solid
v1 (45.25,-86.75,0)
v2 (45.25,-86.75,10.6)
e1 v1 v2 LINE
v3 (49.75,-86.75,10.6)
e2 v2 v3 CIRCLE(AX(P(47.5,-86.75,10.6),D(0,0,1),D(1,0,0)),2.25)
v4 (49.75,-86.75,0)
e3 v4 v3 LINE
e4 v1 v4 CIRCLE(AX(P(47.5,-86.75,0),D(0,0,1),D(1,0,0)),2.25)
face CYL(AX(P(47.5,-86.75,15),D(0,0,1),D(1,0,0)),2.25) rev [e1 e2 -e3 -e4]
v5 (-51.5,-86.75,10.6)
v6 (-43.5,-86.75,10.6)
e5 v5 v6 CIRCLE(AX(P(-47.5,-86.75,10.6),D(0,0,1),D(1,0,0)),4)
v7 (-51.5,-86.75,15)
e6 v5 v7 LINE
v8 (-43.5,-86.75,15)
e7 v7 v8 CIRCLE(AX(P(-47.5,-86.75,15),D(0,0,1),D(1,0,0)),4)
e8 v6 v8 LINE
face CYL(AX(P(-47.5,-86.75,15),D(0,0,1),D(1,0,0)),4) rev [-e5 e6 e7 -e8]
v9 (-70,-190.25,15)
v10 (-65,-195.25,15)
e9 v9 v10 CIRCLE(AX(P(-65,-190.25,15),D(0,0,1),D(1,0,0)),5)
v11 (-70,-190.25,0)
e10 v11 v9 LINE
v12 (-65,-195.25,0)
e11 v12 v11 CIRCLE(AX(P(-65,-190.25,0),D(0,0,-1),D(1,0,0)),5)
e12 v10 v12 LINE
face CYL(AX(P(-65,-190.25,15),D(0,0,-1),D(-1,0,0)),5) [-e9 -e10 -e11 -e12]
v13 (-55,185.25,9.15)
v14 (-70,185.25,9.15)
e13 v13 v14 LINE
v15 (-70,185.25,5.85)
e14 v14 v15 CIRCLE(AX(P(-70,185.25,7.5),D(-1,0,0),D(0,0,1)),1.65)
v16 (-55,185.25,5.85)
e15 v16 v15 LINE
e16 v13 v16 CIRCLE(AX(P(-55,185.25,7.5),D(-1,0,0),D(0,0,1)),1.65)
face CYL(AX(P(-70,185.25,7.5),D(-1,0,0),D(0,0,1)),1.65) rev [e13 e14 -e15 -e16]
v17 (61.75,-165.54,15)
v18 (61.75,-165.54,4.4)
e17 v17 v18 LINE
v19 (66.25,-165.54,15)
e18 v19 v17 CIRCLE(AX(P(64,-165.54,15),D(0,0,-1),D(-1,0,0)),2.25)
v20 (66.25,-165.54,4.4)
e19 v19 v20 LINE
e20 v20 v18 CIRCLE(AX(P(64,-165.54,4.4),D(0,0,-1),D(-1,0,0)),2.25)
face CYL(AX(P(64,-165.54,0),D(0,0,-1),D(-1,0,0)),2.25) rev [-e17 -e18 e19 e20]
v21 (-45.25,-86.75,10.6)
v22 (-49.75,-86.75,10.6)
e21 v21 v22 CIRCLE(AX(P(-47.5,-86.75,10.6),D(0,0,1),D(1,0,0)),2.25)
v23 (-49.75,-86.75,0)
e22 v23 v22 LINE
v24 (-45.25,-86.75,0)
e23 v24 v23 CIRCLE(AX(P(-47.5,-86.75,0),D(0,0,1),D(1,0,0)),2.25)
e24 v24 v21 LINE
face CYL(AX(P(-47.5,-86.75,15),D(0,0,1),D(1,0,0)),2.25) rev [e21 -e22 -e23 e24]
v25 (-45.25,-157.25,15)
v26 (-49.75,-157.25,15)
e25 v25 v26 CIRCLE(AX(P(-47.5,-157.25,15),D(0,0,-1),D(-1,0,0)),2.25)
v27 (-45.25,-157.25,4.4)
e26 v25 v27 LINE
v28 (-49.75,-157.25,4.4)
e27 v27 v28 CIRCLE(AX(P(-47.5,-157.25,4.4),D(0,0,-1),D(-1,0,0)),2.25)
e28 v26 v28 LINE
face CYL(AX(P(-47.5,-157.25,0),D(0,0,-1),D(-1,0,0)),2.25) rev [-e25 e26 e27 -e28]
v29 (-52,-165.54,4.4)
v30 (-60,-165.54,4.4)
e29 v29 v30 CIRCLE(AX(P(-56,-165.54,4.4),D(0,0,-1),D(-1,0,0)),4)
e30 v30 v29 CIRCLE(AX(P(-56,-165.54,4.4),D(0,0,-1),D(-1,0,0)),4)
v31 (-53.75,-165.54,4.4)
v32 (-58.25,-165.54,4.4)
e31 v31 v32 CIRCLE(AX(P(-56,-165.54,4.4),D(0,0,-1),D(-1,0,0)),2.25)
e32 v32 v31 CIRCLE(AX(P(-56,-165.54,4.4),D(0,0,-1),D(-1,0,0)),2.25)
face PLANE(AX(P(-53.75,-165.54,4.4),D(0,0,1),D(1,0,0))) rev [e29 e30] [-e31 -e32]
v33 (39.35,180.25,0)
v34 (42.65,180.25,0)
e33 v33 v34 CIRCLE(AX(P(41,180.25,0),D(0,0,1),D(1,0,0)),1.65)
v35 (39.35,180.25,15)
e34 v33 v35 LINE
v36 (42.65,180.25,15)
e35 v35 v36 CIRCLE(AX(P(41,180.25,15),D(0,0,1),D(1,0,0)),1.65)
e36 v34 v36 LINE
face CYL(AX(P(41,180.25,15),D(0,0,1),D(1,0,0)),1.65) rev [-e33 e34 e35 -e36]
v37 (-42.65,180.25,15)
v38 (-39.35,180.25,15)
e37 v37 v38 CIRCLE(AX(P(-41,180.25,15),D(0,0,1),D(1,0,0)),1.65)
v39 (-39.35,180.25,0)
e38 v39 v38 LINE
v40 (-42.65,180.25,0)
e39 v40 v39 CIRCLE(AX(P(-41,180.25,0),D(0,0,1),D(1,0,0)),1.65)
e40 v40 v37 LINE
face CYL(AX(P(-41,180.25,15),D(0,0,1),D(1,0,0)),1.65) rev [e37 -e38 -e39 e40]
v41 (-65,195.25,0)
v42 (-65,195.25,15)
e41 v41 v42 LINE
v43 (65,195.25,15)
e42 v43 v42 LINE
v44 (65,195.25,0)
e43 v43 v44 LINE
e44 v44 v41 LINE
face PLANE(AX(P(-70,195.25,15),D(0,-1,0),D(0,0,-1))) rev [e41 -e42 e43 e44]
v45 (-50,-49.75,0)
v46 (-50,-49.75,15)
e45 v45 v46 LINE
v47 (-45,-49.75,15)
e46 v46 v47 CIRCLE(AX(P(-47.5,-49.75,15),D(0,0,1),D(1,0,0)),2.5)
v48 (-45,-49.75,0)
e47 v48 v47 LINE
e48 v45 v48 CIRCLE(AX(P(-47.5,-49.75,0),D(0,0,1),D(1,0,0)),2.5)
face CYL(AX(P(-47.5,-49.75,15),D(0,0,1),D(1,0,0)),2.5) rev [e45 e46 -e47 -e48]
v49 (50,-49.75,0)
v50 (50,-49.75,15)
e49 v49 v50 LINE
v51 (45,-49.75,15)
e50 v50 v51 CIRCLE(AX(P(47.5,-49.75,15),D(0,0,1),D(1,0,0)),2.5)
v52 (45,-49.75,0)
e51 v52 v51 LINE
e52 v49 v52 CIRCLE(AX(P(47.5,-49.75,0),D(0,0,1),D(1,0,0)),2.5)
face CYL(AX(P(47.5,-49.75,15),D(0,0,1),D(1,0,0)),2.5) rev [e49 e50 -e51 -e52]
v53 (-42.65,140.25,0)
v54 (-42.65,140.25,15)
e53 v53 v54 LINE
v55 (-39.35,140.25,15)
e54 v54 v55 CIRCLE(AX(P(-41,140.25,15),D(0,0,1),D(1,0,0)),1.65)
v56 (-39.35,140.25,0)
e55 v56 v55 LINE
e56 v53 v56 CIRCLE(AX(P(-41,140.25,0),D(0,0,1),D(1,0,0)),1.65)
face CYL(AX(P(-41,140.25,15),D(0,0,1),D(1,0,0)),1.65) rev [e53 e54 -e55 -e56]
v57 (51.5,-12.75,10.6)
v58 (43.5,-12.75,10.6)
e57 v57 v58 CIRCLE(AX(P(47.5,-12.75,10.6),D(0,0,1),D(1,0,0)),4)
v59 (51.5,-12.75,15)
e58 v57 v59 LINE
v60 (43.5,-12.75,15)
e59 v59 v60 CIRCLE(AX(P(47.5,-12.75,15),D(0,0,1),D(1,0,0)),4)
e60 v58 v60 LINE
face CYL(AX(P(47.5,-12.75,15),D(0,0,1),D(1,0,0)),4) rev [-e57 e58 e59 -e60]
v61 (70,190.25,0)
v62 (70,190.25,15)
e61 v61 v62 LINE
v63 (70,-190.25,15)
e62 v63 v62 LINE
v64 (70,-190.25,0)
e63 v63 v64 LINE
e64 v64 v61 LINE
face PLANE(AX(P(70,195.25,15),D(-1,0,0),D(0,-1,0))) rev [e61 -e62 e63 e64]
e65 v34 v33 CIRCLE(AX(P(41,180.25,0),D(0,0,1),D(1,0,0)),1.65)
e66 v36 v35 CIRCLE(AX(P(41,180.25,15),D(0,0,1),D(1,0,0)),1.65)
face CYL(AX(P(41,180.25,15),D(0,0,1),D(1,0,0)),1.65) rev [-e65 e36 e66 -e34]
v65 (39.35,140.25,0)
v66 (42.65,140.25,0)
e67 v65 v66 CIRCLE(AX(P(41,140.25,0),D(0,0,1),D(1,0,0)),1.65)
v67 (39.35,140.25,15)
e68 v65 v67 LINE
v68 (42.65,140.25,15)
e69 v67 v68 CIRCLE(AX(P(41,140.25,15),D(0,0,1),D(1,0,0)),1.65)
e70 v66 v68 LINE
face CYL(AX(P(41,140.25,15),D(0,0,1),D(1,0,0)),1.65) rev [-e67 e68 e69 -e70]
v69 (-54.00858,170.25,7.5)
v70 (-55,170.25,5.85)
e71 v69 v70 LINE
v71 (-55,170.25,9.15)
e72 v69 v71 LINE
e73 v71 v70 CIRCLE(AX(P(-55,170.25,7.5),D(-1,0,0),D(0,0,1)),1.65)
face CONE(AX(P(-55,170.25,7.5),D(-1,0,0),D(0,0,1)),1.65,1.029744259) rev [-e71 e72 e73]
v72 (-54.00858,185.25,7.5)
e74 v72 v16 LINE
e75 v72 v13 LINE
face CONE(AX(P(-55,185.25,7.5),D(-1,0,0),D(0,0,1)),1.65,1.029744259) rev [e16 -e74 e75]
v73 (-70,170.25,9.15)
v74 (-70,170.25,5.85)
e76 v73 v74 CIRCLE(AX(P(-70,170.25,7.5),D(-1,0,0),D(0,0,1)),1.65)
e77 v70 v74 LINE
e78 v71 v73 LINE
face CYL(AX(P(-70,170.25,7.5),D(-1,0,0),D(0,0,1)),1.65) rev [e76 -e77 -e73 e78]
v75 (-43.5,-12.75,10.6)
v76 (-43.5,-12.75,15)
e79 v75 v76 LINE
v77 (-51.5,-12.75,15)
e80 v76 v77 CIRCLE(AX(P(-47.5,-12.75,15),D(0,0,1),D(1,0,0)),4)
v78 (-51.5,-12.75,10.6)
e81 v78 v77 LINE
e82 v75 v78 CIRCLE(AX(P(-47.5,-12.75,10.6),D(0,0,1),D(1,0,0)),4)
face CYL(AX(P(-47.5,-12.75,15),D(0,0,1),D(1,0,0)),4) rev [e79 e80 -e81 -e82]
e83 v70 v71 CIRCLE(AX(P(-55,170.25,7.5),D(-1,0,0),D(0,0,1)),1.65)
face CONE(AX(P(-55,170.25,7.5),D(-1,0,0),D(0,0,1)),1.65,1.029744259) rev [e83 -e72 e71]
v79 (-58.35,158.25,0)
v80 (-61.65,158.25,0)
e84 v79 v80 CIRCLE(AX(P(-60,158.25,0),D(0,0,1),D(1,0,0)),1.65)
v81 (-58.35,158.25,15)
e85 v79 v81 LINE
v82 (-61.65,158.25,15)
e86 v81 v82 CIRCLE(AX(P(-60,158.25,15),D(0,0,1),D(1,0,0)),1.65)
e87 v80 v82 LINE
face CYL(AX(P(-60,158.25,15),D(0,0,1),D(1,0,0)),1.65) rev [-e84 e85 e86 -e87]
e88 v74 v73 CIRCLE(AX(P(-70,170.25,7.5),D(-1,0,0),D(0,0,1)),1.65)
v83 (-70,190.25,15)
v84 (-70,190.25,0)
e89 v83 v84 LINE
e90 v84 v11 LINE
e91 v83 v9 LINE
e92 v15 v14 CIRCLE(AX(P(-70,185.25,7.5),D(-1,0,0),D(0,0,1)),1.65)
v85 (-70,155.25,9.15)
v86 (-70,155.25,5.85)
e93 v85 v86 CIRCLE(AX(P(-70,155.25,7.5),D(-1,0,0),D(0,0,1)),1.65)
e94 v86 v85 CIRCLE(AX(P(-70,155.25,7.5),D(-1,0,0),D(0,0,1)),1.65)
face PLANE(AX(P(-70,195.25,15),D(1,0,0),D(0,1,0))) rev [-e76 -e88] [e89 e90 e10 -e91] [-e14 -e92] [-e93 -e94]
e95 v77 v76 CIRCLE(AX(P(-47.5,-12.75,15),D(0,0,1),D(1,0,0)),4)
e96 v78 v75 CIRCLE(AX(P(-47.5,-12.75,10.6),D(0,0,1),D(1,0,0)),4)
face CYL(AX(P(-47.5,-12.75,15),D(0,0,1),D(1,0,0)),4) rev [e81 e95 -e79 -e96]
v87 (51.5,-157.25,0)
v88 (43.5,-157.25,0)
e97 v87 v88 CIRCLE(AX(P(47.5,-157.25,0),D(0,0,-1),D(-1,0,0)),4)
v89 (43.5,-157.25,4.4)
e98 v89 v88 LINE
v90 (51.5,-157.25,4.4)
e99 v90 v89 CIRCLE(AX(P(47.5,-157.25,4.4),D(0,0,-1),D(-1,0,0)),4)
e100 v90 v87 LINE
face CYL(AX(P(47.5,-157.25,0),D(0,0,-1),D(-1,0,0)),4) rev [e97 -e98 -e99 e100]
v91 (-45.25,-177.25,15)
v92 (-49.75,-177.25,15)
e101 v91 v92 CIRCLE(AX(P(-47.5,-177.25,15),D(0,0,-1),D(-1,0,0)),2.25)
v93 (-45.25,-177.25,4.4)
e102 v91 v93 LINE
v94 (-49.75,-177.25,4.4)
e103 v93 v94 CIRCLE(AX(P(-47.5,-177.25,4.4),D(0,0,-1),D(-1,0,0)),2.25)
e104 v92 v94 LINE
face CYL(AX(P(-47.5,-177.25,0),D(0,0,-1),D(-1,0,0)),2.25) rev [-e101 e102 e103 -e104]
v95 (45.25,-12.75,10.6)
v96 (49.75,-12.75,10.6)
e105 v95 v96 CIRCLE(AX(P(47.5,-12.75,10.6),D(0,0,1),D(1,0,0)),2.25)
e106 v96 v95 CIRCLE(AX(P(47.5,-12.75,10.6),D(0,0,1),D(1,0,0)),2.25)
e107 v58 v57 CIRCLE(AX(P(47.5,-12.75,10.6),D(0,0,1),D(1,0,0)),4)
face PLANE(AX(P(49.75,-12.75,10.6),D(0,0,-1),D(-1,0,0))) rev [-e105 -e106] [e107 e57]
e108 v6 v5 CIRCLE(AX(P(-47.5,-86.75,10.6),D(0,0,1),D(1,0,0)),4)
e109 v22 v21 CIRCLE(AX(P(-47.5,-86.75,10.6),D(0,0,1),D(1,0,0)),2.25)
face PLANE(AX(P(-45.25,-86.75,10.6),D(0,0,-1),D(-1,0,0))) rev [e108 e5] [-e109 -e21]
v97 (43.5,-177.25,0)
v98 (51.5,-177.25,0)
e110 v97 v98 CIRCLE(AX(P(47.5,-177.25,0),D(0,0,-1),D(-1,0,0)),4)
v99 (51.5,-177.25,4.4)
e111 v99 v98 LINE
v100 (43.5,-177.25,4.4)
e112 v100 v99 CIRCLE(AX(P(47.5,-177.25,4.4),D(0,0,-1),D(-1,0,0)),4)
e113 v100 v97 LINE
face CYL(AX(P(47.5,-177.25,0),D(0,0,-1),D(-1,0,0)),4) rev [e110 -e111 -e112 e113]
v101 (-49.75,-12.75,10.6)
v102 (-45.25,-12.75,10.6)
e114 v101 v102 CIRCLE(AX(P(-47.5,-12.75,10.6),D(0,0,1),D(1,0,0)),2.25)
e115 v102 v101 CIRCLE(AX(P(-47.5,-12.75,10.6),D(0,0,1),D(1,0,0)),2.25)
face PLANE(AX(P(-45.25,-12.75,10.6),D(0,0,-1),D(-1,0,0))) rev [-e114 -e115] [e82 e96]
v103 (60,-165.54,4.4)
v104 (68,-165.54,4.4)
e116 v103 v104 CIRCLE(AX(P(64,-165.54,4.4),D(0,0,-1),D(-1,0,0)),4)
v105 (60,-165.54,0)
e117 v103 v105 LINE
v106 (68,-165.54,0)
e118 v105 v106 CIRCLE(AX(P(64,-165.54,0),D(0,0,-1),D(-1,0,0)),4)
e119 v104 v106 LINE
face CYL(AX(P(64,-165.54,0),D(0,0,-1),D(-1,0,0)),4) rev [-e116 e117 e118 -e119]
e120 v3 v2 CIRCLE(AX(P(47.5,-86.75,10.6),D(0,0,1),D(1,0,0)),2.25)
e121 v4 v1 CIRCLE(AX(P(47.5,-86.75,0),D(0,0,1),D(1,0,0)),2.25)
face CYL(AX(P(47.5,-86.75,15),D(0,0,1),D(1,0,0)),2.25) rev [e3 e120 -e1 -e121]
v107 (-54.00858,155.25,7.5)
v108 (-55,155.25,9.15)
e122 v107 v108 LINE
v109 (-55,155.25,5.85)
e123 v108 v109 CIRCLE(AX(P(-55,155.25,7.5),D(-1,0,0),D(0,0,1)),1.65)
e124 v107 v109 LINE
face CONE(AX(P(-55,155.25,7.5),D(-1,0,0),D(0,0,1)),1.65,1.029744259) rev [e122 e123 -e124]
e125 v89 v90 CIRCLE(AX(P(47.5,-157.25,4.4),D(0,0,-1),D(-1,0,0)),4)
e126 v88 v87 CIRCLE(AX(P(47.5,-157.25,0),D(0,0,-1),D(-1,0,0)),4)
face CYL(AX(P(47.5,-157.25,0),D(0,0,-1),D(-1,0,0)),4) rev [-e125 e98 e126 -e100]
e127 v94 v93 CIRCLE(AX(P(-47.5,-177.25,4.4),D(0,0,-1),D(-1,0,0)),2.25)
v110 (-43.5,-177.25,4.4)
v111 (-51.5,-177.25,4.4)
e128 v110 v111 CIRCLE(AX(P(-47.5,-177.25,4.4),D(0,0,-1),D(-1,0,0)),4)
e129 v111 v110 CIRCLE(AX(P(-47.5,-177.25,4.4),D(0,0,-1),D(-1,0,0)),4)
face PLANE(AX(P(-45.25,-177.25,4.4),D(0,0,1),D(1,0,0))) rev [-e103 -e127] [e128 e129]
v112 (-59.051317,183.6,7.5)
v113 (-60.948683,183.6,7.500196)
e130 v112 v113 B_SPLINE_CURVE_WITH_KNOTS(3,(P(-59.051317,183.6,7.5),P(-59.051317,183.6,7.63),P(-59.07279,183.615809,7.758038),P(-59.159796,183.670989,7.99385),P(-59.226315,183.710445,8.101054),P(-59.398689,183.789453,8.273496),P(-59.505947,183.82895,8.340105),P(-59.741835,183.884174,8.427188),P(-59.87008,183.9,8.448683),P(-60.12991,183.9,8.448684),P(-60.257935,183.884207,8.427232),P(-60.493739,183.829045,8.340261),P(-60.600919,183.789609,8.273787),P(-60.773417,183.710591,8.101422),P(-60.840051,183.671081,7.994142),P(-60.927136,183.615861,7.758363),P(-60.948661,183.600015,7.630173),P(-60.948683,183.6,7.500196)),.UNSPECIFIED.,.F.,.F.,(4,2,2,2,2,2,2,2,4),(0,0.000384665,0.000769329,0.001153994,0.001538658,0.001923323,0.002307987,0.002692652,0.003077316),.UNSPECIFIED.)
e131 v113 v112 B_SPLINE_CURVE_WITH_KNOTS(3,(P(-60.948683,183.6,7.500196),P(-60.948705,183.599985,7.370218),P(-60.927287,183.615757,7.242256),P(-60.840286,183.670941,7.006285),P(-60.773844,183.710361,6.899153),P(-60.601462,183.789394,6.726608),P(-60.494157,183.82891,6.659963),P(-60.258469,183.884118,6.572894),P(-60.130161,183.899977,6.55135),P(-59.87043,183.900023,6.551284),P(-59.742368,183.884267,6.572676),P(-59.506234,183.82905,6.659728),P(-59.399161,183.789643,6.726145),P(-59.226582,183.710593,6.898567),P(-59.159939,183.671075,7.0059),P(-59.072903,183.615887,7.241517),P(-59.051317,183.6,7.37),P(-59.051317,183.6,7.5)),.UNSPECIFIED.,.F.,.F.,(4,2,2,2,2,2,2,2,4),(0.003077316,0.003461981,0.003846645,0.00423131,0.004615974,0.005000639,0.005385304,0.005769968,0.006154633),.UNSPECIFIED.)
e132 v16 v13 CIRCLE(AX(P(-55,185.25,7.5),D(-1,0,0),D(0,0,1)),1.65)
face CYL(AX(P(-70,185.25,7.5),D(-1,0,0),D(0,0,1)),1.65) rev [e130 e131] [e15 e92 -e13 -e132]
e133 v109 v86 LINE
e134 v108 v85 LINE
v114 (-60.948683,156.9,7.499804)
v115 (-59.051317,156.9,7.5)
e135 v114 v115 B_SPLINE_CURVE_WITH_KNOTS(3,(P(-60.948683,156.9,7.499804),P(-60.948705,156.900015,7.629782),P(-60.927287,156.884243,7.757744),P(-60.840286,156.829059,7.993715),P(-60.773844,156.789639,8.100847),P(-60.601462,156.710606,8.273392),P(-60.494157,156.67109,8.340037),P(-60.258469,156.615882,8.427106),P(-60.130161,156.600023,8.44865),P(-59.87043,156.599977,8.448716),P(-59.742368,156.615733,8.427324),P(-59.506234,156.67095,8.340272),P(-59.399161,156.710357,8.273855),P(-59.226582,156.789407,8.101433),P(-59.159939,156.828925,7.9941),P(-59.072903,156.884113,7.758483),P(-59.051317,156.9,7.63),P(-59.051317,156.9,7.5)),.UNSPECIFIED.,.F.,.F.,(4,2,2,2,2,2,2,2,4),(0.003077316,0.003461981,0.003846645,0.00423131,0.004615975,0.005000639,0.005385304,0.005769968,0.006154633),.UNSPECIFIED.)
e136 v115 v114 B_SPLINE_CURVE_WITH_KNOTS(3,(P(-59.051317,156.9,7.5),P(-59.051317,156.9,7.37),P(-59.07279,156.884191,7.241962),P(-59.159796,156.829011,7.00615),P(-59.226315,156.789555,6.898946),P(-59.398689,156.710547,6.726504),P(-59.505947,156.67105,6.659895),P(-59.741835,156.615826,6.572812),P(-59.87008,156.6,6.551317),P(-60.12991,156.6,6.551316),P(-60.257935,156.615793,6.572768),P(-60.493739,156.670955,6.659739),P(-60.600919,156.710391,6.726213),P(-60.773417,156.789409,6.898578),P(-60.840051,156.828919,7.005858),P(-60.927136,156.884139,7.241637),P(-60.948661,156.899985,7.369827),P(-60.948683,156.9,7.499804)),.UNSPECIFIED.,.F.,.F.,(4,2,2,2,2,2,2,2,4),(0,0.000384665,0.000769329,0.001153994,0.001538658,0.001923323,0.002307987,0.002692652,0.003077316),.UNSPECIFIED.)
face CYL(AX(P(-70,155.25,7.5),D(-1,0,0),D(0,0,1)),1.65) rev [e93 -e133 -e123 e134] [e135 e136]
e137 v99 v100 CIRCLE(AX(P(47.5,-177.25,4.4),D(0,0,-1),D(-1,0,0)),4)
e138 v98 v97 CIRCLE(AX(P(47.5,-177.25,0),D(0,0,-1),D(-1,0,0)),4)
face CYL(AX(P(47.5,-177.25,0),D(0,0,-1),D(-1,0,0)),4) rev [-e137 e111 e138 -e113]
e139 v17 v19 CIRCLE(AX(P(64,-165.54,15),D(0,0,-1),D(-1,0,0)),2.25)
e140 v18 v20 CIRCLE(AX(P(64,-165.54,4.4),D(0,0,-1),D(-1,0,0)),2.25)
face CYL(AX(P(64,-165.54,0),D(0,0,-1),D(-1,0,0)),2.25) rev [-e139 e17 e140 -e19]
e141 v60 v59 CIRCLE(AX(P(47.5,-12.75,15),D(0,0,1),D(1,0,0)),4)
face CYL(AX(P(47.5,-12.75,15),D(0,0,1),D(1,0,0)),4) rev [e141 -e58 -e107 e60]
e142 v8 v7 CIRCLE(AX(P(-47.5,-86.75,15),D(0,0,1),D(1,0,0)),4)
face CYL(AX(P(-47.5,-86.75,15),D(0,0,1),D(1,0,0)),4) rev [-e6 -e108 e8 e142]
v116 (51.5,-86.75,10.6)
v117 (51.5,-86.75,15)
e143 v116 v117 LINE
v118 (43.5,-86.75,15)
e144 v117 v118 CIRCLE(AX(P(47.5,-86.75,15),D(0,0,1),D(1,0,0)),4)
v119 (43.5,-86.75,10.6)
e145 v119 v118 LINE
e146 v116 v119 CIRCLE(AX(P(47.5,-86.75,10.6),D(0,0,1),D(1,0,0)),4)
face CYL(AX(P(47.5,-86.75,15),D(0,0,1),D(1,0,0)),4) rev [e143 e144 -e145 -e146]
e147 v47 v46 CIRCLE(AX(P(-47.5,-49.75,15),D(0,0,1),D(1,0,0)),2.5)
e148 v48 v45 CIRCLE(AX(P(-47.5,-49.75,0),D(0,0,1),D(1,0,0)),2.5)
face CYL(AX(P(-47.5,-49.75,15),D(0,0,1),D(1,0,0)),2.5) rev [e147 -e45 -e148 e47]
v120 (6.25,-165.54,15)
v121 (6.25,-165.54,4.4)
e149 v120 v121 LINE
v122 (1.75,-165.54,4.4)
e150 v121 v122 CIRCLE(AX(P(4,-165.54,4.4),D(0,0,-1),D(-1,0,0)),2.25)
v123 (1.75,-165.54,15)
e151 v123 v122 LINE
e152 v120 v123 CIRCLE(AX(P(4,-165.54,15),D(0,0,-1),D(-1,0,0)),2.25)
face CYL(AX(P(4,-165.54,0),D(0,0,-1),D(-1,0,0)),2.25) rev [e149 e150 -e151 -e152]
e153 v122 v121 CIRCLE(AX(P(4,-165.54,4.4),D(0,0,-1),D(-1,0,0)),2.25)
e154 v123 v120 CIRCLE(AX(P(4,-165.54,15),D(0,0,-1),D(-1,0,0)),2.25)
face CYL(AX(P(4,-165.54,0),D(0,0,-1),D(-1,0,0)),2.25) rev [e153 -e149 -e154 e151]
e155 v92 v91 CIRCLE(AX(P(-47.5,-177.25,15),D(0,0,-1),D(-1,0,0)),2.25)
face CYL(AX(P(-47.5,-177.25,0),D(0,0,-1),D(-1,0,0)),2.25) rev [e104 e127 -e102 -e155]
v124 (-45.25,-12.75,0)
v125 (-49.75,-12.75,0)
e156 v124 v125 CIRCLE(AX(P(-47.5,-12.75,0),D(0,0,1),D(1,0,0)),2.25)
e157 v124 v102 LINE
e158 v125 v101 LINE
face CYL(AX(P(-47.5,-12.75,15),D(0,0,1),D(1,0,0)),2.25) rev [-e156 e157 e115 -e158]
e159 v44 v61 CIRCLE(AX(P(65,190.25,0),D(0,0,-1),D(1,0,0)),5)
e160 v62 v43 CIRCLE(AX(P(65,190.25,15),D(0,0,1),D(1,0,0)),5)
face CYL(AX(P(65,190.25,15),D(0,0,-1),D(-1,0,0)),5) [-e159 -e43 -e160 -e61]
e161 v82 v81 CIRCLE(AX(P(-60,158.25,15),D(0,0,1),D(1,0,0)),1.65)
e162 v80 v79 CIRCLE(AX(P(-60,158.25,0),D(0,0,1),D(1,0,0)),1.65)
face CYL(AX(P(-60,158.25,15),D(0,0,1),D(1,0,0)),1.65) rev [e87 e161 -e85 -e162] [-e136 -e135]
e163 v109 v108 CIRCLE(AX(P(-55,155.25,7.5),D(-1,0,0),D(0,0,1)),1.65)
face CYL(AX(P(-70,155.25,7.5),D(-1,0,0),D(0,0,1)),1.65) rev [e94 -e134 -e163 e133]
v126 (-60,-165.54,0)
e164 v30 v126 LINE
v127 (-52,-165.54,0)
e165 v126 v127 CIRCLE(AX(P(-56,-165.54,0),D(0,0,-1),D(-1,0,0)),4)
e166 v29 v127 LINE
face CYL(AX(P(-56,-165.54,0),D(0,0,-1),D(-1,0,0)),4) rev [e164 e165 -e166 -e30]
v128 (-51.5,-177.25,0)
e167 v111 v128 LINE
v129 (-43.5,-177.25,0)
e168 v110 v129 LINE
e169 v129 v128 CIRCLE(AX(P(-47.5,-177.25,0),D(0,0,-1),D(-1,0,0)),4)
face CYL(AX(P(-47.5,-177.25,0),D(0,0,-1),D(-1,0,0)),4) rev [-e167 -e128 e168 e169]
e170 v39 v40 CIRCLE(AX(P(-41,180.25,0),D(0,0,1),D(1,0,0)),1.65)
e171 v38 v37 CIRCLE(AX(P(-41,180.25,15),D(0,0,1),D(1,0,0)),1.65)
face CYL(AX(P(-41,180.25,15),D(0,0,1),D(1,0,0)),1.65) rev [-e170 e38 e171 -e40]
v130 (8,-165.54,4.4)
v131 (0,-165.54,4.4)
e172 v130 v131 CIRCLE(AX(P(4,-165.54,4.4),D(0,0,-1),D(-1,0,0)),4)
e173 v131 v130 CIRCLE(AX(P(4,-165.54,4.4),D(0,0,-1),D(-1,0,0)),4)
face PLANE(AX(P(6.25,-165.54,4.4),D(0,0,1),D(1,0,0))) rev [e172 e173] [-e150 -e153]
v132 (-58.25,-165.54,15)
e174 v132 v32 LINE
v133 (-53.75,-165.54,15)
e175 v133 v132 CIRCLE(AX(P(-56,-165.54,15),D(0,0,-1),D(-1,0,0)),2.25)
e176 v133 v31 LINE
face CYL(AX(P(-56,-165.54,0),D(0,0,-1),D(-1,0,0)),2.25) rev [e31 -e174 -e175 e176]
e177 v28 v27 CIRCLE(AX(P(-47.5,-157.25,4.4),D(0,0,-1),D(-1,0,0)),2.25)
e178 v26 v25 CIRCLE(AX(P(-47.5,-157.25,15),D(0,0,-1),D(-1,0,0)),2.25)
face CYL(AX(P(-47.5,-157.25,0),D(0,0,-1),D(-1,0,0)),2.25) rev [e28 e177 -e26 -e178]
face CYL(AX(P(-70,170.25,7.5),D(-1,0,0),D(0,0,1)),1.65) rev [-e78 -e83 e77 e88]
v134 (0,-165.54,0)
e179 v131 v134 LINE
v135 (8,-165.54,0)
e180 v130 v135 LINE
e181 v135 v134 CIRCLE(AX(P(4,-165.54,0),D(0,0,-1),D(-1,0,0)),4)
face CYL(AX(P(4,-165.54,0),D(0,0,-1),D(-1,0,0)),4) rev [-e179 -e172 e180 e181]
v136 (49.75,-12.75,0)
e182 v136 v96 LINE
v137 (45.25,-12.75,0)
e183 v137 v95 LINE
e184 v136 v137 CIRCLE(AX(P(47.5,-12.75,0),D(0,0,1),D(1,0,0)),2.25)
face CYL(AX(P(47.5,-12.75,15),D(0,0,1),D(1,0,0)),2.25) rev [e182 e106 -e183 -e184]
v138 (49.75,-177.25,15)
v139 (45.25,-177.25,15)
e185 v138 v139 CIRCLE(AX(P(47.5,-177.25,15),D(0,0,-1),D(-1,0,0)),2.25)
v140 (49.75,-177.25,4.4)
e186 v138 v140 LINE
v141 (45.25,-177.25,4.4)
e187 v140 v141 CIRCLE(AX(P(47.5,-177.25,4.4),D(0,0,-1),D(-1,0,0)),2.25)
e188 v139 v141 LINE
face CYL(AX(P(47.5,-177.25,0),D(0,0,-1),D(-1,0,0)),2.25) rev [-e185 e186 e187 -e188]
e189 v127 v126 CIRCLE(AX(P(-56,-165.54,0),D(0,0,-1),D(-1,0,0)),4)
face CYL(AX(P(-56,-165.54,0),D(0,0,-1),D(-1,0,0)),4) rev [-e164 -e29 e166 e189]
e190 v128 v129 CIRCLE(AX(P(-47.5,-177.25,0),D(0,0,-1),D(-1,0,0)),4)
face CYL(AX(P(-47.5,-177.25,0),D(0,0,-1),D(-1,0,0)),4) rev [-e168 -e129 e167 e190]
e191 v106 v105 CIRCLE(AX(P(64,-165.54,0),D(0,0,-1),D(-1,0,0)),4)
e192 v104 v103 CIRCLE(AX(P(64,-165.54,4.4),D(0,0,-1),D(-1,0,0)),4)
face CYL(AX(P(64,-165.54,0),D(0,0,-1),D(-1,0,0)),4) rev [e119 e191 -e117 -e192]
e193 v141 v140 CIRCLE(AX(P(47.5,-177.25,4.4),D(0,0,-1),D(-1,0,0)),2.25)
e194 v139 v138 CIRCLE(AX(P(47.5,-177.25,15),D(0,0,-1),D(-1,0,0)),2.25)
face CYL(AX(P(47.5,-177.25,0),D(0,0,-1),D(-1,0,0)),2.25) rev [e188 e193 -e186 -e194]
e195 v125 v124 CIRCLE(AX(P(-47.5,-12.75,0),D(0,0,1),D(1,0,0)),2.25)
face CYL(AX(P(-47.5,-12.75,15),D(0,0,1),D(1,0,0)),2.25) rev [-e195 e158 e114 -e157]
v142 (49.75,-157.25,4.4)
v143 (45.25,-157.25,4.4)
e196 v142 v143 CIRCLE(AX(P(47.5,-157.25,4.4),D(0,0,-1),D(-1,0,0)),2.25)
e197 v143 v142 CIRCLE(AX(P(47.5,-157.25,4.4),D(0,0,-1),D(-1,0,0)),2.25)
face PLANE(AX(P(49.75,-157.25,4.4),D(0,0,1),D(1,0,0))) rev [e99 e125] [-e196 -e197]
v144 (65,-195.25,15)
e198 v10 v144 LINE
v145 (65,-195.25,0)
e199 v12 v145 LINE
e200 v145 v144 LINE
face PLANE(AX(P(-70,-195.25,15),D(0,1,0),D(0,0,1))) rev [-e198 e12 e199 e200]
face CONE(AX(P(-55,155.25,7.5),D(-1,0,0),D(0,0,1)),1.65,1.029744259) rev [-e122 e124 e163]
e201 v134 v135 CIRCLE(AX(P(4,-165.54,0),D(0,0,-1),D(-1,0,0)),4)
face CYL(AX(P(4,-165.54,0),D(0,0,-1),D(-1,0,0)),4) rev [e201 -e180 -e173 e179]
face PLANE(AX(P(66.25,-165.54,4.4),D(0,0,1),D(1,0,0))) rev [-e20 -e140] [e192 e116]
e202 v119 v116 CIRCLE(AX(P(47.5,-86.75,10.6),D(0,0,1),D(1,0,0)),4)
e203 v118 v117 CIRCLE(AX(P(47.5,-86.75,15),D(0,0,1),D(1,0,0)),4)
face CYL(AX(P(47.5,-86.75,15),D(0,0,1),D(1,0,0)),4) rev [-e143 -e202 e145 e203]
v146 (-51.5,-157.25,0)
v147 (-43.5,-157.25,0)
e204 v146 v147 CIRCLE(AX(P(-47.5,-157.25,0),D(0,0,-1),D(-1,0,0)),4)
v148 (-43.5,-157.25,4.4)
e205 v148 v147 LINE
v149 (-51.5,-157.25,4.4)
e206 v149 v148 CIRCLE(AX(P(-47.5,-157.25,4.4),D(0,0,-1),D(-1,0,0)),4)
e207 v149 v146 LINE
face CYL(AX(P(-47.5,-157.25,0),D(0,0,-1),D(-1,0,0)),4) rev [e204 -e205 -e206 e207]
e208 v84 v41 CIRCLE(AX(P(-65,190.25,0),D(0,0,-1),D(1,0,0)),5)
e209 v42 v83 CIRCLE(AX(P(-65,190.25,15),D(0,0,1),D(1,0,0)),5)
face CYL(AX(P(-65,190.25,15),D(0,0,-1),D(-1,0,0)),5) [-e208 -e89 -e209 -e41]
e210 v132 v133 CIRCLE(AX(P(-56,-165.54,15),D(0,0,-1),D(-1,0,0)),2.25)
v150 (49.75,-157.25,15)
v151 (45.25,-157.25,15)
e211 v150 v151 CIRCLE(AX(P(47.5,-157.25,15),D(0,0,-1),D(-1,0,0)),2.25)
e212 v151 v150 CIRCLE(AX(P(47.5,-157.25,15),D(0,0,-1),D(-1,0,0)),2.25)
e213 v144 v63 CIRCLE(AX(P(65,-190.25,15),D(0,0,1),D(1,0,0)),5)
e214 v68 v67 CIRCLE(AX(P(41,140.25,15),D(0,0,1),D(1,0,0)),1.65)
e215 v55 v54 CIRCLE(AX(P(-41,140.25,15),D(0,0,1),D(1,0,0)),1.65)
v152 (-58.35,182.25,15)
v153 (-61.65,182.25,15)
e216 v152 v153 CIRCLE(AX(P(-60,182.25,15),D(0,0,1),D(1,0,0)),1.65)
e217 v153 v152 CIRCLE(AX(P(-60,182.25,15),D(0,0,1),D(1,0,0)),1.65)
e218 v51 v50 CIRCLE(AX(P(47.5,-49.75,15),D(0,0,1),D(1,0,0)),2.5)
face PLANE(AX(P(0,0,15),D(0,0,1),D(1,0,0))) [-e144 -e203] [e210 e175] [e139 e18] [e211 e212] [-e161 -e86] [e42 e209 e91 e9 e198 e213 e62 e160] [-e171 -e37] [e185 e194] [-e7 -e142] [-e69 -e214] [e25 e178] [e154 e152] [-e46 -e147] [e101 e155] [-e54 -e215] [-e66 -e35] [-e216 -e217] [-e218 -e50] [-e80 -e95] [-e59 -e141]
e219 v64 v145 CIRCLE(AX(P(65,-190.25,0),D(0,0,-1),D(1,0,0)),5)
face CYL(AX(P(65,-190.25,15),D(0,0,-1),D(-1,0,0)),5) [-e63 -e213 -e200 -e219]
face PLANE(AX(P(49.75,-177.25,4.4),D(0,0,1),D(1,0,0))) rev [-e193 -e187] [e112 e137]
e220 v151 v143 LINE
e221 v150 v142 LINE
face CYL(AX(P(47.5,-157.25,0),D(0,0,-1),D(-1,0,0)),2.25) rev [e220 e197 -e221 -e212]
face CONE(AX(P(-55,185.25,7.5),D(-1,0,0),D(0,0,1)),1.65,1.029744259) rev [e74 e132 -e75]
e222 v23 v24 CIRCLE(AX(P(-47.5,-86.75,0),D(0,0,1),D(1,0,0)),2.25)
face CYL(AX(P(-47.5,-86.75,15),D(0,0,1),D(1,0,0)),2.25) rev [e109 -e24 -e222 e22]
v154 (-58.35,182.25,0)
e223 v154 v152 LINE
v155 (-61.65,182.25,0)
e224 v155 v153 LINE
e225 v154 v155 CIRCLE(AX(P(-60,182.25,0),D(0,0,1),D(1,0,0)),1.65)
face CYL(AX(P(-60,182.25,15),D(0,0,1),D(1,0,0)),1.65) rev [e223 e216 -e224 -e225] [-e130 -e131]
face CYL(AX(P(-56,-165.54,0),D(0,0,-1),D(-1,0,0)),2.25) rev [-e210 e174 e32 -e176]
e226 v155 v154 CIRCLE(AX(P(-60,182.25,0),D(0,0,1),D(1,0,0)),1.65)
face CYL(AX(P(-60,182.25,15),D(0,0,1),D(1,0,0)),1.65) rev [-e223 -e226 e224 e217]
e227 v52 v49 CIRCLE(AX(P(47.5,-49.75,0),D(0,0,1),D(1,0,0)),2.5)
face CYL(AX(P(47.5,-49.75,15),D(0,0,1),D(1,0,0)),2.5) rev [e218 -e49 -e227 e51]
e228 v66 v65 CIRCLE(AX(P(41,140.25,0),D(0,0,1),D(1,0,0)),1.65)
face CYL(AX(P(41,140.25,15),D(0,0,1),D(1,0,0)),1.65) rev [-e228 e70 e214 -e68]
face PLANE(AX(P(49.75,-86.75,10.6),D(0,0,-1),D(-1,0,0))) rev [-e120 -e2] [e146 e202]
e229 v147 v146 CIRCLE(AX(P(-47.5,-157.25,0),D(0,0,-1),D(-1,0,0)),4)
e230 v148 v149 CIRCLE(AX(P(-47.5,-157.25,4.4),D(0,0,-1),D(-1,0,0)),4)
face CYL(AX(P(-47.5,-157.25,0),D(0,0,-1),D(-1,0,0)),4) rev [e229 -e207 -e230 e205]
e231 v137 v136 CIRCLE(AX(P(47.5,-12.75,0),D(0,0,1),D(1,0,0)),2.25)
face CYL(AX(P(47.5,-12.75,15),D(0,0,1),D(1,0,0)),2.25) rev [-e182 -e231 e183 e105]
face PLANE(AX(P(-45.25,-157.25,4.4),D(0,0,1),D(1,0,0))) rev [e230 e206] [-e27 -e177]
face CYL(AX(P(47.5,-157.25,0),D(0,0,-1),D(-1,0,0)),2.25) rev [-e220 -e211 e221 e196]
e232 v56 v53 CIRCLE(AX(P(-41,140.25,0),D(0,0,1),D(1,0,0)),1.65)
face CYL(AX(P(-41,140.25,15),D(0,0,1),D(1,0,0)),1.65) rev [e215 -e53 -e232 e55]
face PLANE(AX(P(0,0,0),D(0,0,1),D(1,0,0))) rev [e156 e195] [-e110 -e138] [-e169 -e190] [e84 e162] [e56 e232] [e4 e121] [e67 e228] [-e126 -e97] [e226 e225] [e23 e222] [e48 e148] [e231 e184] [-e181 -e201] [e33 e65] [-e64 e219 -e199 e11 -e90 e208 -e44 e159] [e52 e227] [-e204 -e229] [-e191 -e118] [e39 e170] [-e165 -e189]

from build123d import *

# Parameters (mm, degrees)
SKETCH_1_W                   = 140
SKETCH_1_H                   = 390.5
EXTRUDE_1_DEPTH              = 15
HOLE_WIZARD_M5_6_D           = 4.5
HOLE_WIZARD_M5_6_CBORE_D     = 8
HOLE_WIZARD_M5_6_CBORE_DEPTH = 4.4
HOLE_WIZARD_5_0_5_1_D        = 5
FILLET_1_R                   = 5
HOLE_WIZARD_M4_3_D           = 3.3
HOLE_WIZARD_M4_1_D           = 4.5
HOLE_WIZARD_M4_1_CBORE_D     = 8
HOLE_WIZARD_M4_1_CBORE_DEPTH = 4.4
HOLE_WIZARD_M4_6_D           = 3.3
HOLE_WIZARD_M4_6_DEPTH       = 15
HOLE_WIZARD_M4_6_TIP         = 0.991420021
HOLE_WIZARD_M4_7_D           = 3.3
HOLE_WIZARD_M4_2_D           = 4.5
HOLE_WIZARD_M4_2_CBORE_D     = 8
HOLE_WIZARD_M4_2_CBORE_DEPTH = 4.4


with BuildPart() as part:
    # 草图1 → 凸台-拉伸1 (new body)
    with BuildSketch(Plane.XY):
        Rectangle(SKETCH_1_W, SKETCH_1_H)
    extrude(amount=EXTRUDE_1_DEPTH)

    # M5 六角凹头螺钉的柱形沉头孔6 (through all)
    with Locations(Plane.XY.offset(15)):
        with Locations((-47.5, -12.75), (-47.5, -86.75), (47.5, -12.75), (47.5, -86.75)):
            CounterBoreHole(HOLE_WIZARD_M5_6_D / 2, HOLE_WIZARD_M5_6_CBORE_D / 2, HOLE_WIZARD_M5_6_CBORE_DEPTH)

    # Ø5.0 (5) 直径孔1 (through all)
    with Locations(Plane.XY.offset(15)):
        with Locations((-47.5, -49.75), (47.5, -49.75)):
            Hole(HOLE_WIZARD_5_0_5_1_D / 2)

    # 圆角1
    fillet_1_edges = [part.edges().sort_by_distance(p)[0] for p in [
        (70, -195.25, 7.5),
        (-70, -195.25, 7.5),
        (-70, 195.25, 7.5),
        (70, 195.25, 7.5),
    ]]
    fillet(fillet_1_edges, radius=FILLET_1_R)

    # M4 螺纹孔3 (through all)
    with Locations(Plane.XY.offset(15)):
        with Locations((-41, 180.25), (41, 180.25), (41, 140.25), (-41, 140.25)):
            Hole(HOLE_WIZARD_M4_3_D / 2)

    # M4 六角凹头螺钉的柱形沉头孔1 (through all)
    with Locations(Plane(origin=(0, 0, 0), x_dir=(-1, 0, 0), z_dir=(0, 0, -1))):
        with Locations((47.5, -157.25), (47.5, -177.25), (-47.5, -157.25), (-47.5, -177.25)):
            CounterBoreHole(HOLE_WIZARD_M4_1_D / 2, HOLE_WIZARD_M4_1_CBORE_D / 2, HOLE_WIZARD_M4_1_CBORE_DEPTH)

    # M4 螺纹孔6
    with Locations(Plane.ZY.offset(70)):
        with Locations((7.5, 185.25), (7.5, 170.25), (7.5, 155.25)):
            Hole(HOLE_WIZARD_M4_6_D / 2, depth=HOLE_WIZARD_M4_6_DEPTH)
            with Locations((0, 0, -(HOLE_WIZARD_M4_6_DEPTH + HOLE_WIZARD_M4_6_TIP / 2))):  # 118° drill point
                Cone(0, HOLE_WIZARD_M4_6_D / 2, HOLE_WIZARD_M4_6_TIP, mode=Mode.SUBTRACT)

    # M4 螺纹孔7 (through all)
    with Locations(Plane.XY.offset(15)):
        with Locations((-60, 182.25), (-60, 158.25)):
            Hole(HOLE_WIZARD_M4_7_D / 2)

    # M4 六角凹头螺钉的柱形沉头孔2 (through all)
    with Locations(Plane(origin=(0, 0, 0), x_dir=(-1, 0, 0), z_dir=(0, 0, -1))):
        with Locations((-64, -165.54), (-4, -165.54), (-64, -225.54), (-4, -225.54), (56, -165.54), (56, -225.54)):
            CounterBoreHole(HOLE_WIZARD_M4_2_D / 2, HOLE_WIZARD_M4_2_CBORE_D / 2, HOLE_WIZARD_M4_2_CBORE_DEPTH)


solid = part.part
